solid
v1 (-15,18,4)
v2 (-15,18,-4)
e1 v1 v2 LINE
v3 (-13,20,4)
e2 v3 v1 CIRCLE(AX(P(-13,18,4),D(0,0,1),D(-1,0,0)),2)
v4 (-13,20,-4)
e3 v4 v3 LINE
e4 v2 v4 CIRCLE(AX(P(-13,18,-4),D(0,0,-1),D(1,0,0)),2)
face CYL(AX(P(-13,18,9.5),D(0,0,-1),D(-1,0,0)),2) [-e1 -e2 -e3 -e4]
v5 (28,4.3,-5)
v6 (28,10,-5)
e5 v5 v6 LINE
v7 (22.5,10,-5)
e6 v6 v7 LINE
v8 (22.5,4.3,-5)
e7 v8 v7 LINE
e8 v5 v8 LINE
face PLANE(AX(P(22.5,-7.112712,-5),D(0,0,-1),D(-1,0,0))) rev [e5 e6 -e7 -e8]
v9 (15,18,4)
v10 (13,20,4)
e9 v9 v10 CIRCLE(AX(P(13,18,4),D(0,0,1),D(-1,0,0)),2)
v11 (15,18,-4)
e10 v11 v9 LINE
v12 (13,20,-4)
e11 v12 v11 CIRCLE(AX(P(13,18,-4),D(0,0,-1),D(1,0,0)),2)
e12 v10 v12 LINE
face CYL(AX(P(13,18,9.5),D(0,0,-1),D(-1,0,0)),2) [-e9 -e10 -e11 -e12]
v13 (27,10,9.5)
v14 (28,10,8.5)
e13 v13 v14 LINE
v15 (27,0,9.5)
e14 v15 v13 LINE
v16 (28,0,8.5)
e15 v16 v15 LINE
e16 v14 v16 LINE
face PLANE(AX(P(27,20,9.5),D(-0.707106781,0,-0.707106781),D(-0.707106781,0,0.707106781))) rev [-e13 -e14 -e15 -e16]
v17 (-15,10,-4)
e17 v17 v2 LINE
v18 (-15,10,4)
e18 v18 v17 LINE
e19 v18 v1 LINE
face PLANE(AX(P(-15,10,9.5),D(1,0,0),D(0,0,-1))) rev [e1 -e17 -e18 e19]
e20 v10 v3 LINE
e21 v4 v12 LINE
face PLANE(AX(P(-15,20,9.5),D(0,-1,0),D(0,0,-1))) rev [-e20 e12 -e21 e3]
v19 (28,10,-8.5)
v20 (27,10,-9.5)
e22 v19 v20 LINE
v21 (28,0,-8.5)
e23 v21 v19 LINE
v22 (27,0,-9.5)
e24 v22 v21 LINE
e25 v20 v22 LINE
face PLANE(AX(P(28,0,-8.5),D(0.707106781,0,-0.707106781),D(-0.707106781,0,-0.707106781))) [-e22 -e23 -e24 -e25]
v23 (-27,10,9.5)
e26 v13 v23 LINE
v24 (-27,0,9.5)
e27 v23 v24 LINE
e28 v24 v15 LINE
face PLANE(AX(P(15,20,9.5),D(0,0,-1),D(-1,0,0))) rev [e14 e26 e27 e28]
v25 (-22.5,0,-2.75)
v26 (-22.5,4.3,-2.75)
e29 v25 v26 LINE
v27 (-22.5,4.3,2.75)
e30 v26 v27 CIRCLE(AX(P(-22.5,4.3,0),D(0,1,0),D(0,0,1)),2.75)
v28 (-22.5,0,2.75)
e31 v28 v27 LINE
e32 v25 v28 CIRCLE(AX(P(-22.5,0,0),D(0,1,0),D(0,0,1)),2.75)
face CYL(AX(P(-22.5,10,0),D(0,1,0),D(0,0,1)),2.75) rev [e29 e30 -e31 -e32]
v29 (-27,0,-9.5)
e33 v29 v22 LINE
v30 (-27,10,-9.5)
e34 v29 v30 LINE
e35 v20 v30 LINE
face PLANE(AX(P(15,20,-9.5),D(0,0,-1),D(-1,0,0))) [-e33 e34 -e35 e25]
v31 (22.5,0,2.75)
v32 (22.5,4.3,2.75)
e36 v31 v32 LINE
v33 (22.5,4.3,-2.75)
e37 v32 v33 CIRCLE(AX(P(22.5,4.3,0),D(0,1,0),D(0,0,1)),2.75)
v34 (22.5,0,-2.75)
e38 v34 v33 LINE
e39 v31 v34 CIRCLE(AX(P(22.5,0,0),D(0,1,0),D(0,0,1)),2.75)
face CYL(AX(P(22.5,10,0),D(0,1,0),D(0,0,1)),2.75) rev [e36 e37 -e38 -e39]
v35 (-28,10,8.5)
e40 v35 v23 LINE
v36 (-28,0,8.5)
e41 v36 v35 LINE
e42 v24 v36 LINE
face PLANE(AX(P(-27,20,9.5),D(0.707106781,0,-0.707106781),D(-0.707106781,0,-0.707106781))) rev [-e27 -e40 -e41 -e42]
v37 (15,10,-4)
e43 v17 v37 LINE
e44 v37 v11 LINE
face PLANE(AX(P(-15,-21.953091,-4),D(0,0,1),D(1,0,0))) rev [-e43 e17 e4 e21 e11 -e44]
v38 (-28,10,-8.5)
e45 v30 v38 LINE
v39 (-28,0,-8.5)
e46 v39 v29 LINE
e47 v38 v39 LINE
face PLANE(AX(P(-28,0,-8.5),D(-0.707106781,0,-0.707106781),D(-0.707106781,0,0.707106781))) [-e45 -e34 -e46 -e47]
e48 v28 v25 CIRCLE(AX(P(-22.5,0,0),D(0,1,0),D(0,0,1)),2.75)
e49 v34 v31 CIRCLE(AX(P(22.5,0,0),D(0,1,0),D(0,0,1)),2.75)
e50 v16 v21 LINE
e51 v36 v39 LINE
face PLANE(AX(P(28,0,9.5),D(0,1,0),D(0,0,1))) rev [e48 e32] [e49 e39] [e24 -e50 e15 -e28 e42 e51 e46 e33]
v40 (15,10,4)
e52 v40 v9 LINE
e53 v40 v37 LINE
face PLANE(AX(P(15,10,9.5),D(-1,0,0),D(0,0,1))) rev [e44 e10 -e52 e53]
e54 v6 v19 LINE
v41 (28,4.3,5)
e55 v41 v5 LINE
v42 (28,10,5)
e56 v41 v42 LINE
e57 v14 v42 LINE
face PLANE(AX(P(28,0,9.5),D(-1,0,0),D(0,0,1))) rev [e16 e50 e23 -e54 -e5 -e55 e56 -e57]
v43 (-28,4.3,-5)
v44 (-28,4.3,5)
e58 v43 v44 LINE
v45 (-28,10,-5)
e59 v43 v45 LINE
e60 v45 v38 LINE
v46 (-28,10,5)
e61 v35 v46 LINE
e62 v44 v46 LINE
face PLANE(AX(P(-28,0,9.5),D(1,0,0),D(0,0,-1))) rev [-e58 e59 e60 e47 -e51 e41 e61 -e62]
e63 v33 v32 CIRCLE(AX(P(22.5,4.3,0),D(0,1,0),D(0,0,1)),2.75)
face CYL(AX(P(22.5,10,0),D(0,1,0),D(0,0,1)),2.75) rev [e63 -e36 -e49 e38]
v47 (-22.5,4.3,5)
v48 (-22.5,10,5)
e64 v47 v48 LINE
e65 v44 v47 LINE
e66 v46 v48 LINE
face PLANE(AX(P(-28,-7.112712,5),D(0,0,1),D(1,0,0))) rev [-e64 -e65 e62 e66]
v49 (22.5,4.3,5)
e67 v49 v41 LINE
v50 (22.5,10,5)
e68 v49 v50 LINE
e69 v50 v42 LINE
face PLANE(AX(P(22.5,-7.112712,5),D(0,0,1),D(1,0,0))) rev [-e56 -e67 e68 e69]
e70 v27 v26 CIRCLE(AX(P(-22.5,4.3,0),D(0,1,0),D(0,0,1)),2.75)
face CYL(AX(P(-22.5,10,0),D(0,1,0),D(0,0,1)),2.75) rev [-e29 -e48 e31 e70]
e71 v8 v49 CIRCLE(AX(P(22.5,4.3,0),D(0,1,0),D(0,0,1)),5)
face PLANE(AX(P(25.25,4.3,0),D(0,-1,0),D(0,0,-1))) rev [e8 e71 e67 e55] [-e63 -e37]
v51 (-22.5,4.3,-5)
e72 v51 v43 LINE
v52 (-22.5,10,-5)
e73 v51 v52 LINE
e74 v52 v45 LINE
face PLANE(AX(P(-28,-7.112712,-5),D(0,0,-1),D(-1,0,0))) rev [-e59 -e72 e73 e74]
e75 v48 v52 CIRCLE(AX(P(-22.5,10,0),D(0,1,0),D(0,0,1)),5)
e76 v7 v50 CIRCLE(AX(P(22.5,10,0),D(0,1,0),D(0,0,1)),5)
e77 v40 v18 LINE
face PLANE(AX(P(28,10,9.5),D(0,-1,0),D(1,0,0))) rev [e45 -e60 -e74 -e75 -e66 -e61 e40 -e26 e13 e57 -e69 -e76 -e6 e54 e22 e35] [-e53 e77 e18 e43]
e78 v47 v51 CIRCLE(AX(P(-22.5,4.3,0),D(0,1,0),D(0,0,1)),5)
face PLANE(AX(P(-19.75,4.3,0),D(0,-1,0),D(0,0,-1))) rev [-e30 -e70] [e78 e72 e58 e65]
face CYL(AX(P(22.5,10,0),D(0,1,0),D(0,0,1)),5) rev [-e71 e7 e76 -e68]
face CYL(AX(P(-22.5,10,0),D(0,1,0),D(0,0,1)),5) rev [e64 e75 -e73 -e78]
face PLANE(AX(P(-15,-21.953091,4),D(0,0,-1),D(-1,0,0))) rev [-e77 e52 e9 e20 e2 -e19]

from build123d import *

# Parameters (mm, degrees)
BOSS_EXTRUDE1_DEPTH                                  = 9.5
HOLE_SIZE_PER_SOCKET_HEAD_CAP_SCREW_TYPE_D           = 5.5
HOLE_SIZE_PER_SOCKET_HEAD_CAP_SCREW_TYPE_CBORE_D     = 10
HOLE_SIZE_PER_SOCKET_HEAD_CAP_SCREW_TYPE_CBORE_DEPTH = 5.7
SKETCH4_W                                            = 5.5
SKETCH4_H                                            = 10
CUT_EXTRUDE1_DEPTH                                   = 5.7
SKETCH5_W                                            = 30
SKETCH5_H                                            = 11
CUT_EXTRUDE2_DEPTH                                   = 10
CHAMFER1_SIZE                                        = 1
FILLET1_R                                            = 2


with BuildPart() as part:
    # Sketch1 → Boss-Extrude1 (new, symmetric)
    with BuildSketch(Plane.XY):
        Polygon((28, 0), (-28, 0), (-28, 10), (-15, 10), (-15, 20), (15, 20), (15, 10), (28, 10), align=None)
    extrude(amount=BOSS_EXTRUDE1_DEPTH, both=True)

    # Hole size per socket head cap screw type 1 (through all)
    with Locations(Plane(origin=(0, 10, 0), x_dir=(-1, 0, 0), z_dir=(0, 1, 0))):
        with Locations((22.5, 0), (-22.5, 0)):
            CounterBoreHole(HOLE_SIZE_PER_SOCKET_HEAD_CAP_SCREW_TYPE_D / 2, HOLE_SIZE_PER_SOCKET_HEAD_CAP_SCREW_TYPE_CBORE_D / 2, HOLE_SIZE_PER_SOCKET_HEAD_CAP_SCREW_TYPE_CBORE_DEPTH)

    # Sketch4 → Cut-Extrude1 (cut)
    with BuildSketch(Plane(origin=(0, 10, 0), x_dir=(1, 0, 0), z_dir=(0, 1, 0))):
        with Locations((-25.25, 0)):
            Rectangle(SKETCH4_W, SKETCH4_H)
        with Locations((25.25, 0)):
            Rectangle(SKETCH4_W, SKETCH4_H)
    extrude(amount=-CUT_EXTRUDE1_DEPTH, mode=Mode.SUBTRACT)

    # Sketch5 → Cut-Extrude2 (cut)
    with BuildSketch(Plane(origin=(0, 20, 0), x_dir=(1, 0, 0), z_dir=(0, 1, 0))):
        with Locations((0, 9.5)):
            Rectangle(SKETCH5_W, SKETCH5_H)
        with Locations((0, -9.5)):
            Rectangle(SKETCH5_W, SKETCH5_H)
    extrude(amount=-CUT_EXTRUDE2_DEPTH, mode=Mode.SUBTRACT)

    # Chamfer1
    chamfer1_edges = [part.edges().sort_by_distance(p)[0] for p in [
        (-28, 5, 9.5),
        (28, 5, 9.5),
        (28, 5, -9.5),
        (-28, 5, -9.5),
    ]]
    chamfer(chamfer1_edges, length=CHAMFER1_SIZE)

    # Fillet1
    fillet1_edges = [part.edges().sort_by_distance(p)[0] for p in [
        (-15, 20, 0),
        (15, 20, 0),
    ]]
    fillet(fillet1_edges, radius=FILLET1_R)


solid = part.part
